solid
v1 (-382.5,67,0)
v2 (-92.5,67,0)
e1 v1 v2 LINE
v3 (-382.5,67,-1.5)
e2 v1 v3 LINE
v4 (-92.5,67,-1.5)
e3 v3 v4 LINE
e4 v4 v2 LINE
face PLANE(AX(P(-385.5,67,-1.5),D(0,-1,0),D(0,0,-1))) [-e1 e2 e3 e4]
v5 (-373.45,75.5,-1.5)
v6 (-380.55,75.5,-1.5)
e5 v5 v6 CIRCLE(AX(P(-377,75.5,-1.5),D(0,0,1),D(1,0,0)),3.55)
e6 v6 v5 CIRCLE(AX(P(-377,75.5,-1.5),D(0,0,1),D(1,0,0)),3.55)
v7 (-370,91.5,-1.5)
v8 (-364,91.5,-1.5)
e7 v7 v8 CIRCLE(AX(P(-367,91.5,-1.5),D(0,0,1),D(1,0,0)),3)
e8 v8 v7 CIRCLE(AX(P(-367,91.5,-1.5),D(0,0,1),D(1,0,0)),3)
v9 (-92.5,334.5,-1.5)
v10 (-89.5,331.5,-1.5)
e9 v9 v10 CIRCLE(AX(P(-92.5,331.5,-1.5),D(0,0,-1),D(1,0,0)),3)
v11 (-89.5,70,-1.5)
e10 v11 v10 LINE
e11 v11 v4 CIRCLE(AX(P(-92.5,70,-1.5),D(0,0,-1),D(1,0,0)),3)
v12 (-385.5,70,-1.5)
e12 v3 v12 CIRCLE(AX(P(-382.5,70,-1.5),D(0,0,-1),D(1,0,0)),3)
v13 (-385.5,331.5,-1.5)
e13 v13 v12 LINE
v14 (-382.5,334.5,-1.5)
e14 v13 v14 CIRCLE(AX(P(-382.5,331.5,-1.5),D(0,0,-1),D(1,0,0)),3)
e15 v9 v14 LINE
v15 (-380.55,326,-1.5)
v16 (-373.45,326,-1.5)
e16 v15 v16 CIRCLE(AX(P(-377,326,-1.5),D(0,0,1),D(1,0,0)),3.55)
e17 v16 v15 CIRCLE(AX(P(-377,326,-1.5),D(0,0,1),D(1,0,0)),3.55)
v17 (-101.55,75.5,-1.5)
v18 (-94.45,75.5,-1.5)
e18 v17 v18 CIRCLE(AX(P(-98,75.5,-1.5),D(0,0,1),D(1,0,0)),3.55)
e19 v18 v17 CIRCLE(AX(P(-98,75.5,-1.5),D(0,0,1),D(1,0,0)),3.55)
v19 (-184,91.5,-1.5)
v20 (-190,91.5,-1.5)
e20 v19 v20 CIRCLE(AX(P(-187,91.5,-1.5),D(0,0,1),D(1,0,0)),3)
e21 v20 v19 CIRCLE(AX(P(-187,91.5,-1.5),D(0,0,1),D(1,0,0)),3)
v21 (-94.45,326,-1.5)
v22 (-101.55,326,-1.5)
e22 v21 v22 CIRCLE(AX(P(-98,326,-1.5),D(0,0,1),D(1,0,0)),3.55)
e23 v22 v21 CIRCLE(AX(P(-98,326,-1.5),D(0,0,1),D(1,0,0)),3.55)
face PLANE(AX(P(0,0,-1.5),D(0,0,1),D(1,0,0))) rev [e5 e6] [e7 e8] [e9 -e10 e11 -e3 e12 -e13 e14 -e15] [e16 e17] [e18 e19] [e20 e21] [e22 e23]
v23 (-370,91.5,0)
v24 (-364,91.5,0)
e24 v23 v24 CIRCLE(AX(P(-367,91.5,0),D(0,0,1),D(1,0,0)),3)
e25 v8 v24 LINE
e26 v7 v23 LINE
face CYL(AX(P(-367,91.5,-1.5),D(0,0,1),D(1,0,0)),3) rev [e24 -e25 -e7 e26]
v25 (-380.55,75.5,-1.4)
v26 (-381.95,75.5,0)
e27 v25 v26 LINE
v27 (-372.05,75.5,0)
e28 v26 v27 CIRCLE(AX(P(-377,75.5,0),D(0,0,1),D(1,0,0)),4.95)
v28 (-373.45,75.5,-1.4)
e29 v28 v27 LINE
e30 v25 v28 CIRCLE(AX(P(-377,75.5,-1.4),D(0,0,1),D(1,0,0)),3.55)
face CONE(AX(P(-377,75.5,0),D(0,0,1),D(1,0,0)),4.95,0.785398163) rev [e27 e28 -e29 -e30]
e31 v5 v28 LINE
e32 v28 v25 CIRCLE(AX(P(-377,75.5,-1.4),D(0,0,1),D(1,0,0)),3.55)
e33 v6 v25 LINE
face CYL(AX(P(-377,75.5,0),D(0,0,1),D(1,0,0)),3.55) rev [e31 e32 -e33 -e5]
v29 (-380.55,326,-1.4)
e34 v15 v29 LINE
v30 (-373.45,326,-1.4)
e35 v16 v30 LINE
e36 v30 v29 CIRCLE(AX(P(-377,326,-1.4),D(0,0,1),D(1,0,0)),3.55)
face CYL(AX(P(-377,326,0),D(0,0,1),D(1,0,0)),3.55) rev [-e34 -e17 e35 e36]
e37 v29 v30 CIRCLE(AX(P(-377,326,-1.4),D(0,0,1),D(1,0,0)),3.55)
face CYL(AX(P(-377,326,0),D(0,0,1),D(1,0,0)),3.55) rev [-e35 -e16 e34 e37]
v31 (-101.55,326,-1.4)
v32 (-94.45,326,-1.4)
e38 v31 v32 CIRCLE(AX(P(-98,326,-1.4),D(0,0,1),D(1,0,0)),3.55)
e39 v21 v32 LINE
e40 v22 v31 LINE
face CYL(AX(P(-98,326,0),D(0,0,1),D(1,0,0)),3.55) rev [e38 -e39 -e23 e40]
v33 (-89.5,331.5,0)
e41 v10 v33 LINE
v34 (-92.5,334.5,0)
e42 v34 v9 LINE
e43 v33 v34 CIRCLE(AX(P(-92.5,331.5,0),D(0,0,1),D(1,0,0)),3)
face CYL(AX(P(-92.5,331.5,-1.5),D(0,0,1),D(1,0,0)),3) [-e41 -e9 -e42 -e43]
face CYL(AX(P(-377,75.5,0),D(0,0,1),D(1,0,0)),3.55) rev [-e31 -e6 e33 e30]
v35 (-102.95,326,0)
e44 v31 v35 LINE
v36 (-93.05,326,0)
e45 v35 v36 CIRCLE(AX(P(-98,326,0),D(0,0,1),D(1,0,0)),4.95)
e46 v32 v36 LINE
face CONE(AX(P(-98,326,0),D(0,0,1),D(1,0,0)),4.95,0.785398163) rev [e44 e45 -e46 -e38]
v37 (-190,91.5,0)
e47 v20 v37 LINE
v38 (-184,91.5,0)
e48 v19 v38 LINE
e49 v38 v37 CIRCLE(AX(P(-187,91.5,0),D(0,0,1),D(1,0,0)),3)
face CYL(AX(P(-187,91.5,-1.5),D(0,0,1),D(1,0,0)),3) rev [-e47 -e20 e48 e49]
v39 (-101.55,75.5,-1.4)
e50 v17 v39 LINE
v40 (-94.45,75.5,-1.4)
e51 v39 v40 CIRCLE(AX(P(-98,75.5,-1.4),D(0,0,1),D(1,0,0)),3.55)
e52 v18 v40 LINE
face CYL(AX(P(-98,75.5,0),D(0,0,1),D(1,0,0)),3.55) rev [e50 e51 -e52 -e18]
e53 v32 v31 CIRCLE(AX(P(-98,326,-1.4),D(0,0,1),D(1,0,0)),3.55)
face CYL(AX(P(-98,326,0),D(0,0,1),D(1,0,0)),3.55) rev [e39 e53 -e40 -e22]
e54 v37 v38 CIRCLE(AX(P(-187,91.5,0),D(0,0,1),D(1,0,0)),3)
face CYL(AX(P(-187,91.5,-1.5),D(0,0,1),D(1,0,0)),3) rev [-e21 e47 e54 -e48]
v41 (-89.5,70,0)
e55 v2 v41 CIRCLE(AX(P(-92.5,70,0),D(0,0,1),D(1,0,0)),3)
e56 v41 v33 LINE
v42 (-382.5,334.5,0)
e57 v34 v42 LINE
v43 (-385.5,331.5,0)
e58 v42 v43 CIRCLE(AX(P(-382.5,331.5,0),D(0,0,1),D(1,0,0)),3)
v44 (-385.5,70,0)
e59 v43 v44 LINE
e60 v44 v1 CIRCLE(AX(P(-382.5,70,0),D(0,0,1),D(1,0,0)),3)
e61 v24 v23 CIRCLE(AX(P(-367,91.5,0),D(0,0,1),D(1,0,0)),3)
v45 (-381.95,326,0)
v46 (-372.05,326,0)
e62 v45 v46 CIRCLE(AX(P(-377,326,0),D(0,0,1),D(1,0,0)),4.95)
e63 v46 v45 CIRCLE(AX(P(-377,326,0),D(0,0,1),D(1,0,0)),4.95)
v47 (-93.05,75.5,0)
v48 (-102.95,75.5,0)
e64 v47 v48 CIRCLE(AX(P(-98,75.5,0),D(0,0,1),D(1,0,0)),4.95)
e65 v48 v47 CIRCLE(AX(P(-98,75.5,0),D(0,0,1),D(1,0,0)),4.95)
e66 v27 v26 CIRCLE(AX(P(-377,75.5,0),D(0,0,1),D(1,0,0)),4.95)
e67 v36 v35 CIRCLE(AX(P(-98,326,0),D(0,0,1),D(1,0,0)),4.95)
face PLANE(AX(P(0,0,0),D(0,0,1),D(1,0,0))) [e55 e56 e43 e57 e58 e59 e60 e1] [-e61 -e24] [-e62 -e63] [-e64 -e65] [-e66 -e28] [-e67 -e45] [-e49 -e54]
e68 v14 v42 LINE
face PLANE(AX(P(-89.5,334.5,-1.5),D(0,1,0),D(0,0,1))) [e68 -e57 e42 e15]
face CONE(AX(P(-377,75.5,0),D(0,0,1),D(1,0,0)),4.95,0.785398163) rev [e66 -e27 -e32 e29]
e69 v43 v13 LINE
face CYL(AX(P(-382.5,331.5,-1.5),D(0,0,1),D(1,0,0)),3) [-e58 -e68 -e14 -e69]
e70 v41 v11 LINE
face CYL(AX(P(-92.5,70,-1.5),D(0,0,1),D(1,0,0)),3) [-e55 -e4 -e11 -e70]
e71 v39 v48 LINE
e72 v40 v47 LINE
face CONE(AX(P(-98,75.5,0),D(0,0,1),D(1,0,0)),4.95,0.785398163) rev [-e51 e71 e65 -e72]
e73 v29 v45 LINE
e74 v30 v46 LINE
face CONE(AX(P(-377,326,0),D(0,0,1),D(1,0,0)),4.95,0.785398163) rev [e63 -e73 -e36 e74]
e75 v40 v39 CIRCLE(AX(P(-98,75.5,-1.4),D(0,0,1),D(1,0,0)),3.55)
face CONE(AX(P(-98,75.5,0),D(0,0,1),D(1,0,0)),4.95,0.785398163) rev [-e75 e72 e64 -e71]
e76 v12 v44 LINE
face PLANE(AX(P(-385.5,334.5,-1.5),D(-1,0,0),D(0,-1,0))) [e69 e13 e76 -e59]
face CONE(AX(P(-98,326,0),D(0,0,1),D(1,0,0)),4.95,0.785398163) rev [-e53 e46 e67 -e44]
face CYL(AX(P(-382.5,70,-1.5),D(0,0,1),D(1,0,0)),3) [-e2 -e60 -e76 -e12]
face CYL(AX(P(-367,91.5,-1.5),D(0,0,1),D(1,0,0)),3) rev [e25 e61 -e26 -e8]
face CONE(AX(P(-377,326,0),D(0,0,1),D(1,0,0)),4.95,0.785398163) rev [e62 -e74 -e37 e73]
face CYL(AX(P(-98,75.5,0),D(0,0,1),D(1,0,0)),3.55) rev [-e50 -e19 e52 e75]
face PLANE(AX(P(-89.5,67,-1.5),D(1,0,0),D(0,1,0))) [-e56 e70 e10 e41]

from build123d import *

# Parameters (mm, degrees)
SKETCH_1_W                       = 296
SKETCH_1_H                       = 267.5
EXTRUDE_1_DEPTH                  = 1.5
HOLE_WIZARD_7_1_7_1_2_AT_2_COUNT = 2
HOLE_WIZARD_7_1_7_1_2_AT_2_PITCH = 250.5
HOLE_WIZARD_7_1_7_1_2_AT_3_COUNT = 2
HOLE_WIZARD_7_1_7_1_2_AT_3_PITCH = 374.9549973
HOLE_WIZARD_7_1_7_1_2_AT_4_COUNT = 2
HOLE_WIZARD_7_1_7_1_2_AT_4_PITCH = 279
FILLET_1_R                       = 3
SKETCH_6_R                       = 3
CUT_EXTRUDE_1_DEPTH              = 1.5


with BuildPart() as part:
    # 草图1 → 凸台-拉伸1 (new body)
    with BuildSketch(Plane.XY):
        with Locations((-237.5, 200.75)):
            Rectangle(SKETCH_1_W, SKETCH_1_H)
    extrude(amount=-EXTRUDE_1_DEPTH)

    # 草图4 → Ø7.1 (7.1) 直径孔2 (revolve, cut)
    with BuildSketch(Plane(origin=(-377, 326, 0), x_dir=(0, -1, 0), z_dir=(1, 0, 0))):
        Polygon((0, 0), (0, 1.5), (3.55, 1.5), (3.55, 1.4), (4.95, 0), align=None)
    hole_wizard_7_1_7_1_2 = revolve(axis=Axis((-377, 326, 6.35), (0, 0, -1)), mode=Mode.SUBTRACT)

    # Ø7.1 (7.1) 直径孔2 at 2: Ø7.1 (7.1) 直径孔2 ×2
    with Locations(*[(0, -i * HOLE_WIZARD_7_1_7_1_2_AT_2_PITCH, 0) for i in range(1, HOLE_WIZARD_7_1_7_1_2_AT_2_COUNT)]):
        add(hole_wizard_7_1_7_1_2, mode=Mode.SUBTRACT)

    # Ø7.1 (7.1) 直径孔2 at 3: Ø7.1 (7.1) 直径孔2 ×2
    with Locations(*[Vector(0.7440892960736261, -0.6680801744316739, 0) * (i * HOLE_WIZARD_7_1_7_1_2_AT_3_PITCH) for i in range(1, HOLE_WIZARD_7_1_7_1_2_AT_3_COUNT)]):
        add(hole_wizard_7_1_7_1_2, mode=Mode.SUBTRACT)

    # Ø7.1 (7.1) 直径孔2 at 4: Ø7.1 (7.1) 直径孔2 ×2
    with Locations(*[(i * HOLE_WIZARD_7_1_7_1_2_AT_4_PITCH, 0, 0) for i in range(1, HOLE_WIZARD_7_1_7_1_2_AT_4_COUNT)]):
        add(hole_wizard_7_1_7_1_2, mode=Mode.SUBTRACT)

    # 圆角1
    fillet_1_edges = [part.edges().sort_by_distance(p)[0] for p in [
        (-385.5, 67, -0.75),
        (-385.5, 334.5, -0.75),
        (-89.5, 334.5, -0.75),
        (-89.5, 67, -0.75),
    ]]
    fillet(fillet_1_edges, radius=FILLET_1_R)

    # 草图6 → 切除-拉伸1 (cut)
    with BuildSketch(Plane.XY):
        with Locations((-367, 91.5)):
            Circle(SKETCH_6_R)
        with Locations((-187, 91.5)):
            Circle(SKETCH_6_R)
    extrude(amount=-CUT_EXTRUDE_1_DEPTH, mode=Mode.SUBTRACT)


solid = part.part
